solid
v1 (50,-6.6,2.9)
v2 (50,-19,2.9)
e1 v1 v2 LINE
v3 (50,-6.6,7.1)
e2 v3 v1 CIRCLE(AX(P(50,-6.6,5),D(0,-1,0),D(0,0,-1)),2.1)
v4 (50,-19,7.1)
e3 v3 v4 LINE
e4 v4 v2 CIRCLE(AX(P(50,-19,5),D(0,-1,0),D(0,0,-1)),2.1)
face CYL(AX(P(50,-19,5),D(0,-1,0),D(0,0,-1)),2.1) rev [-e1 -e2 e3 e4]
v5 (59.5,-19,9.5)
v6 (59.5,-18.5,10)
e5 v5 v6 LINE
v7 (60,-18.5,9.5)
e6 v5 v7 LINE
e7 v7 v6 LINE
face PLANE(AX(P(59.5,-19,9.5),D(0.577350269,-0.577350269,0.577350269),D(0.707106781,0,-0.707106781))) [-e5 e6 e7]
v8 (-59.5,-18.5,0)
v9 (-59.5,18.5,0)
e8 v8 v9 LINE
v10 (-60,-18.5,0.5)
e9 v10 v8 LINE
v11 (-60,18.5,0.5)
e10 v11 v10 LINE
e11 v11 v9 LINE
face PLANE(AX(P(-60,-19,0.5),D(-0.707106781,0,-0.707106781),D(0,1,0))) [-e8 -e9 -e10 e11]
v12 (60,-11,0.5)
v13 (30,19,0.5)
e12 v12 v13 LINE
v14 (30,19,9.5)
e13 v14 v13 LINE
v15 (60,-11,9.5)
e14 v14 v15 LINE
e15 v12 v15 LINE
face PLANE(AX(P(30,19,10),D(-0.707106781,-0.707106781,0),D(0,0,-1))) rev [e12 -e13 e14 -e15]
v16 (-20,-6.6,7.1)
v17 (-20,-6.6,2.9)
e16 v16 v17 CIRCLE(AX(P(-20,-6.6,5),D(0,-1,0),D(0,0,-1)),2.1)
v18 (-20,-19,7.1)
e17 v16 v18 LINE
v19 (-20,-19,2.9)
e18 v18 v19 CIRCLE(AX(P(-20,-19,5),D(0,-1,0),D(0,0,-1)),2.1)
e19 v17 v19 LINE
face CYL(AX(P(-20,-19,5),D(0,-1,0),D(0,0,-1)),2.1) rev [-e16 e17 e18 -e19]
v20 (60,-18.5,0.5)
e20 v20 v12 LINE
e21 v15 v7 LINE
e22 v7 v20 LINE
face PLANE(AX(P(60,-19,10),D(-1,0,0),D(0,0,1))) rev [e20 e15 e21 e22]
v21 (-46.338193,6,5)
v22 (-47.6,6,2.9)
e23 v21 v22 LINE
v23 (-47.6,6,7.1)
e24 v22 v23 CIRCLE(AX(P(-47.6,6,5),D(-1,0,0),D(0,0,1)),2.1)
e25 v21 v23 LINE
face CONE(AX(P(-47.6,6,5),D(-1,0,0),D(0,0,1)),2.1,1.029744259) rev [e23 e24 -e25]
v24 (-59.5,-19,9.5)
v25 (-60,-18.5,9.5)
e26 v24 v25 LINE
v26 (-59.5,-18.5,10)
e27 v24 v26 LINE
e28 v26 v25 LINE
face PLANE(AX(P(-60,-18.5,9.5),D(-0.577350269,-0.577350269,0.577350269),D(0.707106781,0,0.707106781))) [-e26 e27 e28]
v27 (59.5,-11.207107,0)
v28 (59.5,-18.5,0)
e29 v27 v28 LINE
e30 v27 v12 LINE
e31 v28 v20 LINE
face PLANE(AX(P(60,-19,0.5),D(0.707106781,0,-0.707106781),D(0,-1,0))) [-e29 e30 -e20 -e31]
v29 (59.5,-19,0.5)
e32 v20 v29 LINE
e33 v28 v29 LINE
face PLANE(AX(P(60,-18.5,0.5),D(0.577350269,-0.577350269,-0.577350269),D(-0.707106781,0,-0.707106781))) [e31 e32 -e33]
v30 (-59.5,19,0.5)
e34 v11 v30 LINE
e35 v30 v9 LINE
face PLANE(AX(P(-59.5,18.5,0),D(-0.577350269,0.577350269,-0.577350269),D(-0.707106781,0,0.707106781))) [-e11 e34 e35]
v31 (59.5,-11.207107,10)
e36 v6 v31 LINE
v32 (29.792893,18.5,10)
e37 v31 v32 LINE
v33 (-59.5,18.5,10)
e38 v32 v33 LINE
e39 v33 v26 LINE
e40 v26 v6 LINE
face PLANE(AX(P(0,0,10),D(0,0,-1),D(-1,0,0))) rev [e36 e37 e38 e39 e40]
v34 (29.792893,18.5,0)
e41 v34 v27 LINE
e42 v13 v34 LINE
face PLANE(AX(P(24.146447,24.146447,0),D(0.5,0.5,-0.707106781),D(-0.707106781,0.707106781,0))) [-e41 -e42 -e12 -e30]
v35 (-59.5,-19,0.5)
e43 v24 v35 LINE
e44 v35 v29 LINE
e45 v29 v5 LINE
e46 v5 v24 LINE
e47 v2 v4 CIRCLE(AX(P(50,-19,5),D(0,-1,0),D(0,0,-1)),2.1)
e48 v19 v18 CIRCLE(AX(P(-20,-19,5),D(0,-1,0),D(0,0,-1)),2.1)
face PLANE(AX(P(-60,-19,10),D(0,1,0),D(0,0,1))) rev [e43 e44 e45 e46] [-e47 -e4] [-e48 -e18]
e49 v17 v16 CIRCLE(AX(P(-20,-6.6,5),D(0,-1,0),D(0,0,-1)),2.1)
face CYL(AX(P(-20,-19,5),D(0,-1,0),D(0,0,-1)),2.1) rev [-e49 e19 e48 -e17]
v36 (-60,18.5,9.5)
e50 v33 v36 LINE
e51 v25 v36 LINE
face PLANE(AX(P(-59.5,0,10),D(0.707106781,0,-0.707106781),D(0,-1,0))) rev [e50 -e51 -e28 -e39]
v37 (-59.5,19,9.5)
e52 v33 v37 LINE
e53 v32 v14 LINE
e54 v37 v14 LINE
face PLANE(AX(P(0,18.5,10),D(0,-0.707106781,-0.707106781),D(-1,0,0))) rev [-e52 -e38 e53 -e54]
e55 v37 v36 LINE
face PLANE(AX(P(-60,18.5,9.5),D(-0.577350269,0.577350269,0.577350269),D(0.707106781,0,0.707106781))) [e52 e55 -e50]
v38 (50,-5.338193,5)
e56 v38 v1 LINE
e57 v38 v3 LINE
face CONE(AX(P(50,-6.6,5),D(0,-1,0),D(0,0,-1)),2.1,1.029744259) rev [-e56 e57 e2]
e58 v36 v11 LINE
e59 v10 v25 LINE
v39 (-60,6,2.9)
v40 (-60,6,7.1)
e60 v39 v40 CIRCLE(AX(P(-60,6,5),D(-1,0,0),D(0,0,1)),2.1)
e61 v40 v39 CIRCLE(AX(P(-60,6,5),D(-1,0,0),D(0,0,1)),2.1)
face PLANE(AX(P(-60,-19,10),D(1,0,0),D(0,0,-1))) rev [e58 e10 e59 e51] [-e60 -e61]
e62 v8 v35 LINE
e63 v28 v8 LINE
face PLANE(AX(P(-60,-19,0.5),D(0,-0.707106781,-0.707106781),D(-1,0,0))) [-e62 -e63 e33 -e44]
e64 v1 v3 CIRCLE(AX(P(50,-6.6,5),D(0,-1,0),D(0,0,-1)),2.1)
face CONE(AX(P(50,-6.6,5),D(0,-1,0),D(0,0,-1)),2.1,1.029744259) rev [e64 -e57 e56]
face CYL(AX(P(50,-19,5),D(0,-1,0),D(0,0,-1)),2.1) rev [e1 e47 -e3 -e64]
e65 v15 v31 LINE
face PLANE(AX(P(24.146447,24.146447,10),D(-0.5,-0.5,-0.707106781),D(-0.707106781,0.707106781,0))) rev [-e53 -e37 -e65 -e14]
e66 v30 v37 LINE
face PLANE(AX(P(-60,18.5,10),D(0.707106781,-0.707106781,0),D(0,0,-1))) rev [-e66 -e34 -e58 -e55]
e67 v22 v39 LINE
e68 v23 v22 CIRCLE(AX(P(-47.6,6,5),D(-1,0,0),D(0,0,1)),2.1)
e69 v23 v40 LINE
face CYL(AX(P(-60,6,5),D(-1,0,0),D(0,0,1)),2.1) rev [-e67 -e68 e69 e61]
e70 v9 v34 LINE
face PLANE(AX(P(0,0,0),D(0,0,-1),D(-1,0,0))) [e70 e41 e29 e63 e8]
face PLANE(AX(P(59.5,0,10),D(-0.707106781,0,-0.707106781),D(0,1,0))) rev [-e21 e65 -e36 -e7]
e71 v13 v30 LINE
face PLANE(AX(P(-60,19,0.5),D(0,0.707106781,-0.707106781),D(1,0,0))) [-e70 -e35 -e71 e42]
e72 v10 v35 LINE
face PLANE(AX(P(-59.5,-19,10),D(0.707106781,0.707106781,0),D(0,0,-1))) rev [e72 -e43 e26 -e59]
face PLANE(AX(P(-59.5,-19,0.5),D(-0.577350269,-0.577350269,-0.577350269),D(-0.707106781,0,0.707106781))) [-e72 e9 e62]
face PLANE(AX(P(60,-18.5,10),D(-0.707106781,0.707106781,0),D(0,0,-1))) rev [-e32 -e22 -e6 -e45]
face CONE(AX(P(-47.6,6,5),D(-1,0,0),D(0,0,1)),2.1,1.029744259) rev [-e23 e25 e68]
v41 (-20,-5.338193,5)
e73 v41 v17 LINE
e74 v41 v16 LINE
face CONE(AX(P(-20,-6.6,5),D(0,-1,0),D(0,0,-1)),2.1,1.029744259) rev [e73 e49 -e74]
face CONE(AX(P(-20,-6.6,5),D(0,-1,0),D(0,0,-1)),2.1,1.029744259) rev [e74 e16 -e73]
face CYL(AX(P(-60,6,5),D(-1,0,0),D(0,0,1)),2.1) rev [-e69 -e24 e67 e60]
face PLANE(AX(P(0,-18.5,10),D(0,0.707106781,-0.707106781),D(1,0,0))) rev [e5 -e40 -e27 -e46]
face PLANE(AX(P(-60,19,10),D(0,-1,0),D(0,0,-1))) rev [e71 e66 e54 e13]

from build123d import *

# Parameters (mm, degrees)
SKETCH_1_W             = 120
SKETCH_1_H             = 38
EXTRUDE_1_DEPTH        = 10
CHAMFER_1_SIZE         = 30
HOLE_WIZARD_M5_1_D     = 4.2
HOLE_WIZARD_M5_1_DEPTH = 12.4
HOLE_WIZARD_M5_1_TIP   = 1.2618073
HOLE_WIZARD_M5_2_D     = 4.2
HOLE_WIZARD_M5_2_DEPTH = 12.4
HOLE_WIZARD_M5_2_TIP   = 1.2618073
CHAMFER_2_SIZE         = 0.5


with BuildPart() as part:
    # 草图1 → 凸台-拉伸1 (new body)
    with BuildSketch(Plane.XY):
        Rectangle(SKETCH_1_W, SKETCH_1_H)
    extrude(amount=EXTRUDE_1_DEPTH)

    # 倒角1
    chamfer_1_edges = [part.edges().sort_by_distance(p)[0] for p in [
        (60, 19, 5),
    ]]
    chamfer(chamfer_1_edges, length=CHAMFER_1_SIZE)

    # M5 螺纹孔1
    with Locations(Plane.ZY.offset(60)):
        with Locations((5, 6)):
            Hole(HOLE_WIZARD_M5_1_D / 2, depth=HOLE_WIZARD_M5_1_DEPTH)
            with Locations((0, 0, -(HOLE_WIZARD_M5_1_DEPTH + HOLE_WIZARD_M5_1_TIP / 2))):  # 118° drill point
                Cone(0, HOLE_WIZARD_M5_1_D / 2, HOLE_WIZARD_M5_1_TIP, mode=Mode.SUBTRACT)

    # M5 螺纹孔2
    with Locations(Plane(origin=(0, -19, 0), x_dir=(-1, 0, 0), z_dir=(0, -1, 0))):
        with Locations((-50, -5), (20, -5)):
            Hole(HOLE_WIZARD_M5_2_D / 2, depth=HOLE_WIZARD_M5_2_DEPTH)
            with Locations((0, 0, -(HOLE_WIZARD_M5_2_DEPTH + HOLE_WIZARD_M5_2_TIP / 2))):  # 118° drill point
                Cone(0, HOLE_WIZARD_M5_2_D / 2, HOLE_WIZARD_M5_2_TIP, mode=Mode.SUBTRACT)

    # 倒角2
    chamfer_2_edges = [part.edges().sort_by_distance(p)[0] for p in [
        (-60, 0, 10),
        (-15, 19, 0),
        (-15, 19, 10),
        (45, 4, 0),
        (45, 4, 10),
        (0, -19, 10),
        (60, -15, 10),
        (0, -19, 0),
        (-60, 0, 0),
        (60, -15, 0),
        (60, -19, 5),
        (-60, -19, 5),
        (-60, 19, 5),
    ]]
    chamfer(chamfer_2_edges, length=CHAMFER_2_SIZE)


solid = part.part
